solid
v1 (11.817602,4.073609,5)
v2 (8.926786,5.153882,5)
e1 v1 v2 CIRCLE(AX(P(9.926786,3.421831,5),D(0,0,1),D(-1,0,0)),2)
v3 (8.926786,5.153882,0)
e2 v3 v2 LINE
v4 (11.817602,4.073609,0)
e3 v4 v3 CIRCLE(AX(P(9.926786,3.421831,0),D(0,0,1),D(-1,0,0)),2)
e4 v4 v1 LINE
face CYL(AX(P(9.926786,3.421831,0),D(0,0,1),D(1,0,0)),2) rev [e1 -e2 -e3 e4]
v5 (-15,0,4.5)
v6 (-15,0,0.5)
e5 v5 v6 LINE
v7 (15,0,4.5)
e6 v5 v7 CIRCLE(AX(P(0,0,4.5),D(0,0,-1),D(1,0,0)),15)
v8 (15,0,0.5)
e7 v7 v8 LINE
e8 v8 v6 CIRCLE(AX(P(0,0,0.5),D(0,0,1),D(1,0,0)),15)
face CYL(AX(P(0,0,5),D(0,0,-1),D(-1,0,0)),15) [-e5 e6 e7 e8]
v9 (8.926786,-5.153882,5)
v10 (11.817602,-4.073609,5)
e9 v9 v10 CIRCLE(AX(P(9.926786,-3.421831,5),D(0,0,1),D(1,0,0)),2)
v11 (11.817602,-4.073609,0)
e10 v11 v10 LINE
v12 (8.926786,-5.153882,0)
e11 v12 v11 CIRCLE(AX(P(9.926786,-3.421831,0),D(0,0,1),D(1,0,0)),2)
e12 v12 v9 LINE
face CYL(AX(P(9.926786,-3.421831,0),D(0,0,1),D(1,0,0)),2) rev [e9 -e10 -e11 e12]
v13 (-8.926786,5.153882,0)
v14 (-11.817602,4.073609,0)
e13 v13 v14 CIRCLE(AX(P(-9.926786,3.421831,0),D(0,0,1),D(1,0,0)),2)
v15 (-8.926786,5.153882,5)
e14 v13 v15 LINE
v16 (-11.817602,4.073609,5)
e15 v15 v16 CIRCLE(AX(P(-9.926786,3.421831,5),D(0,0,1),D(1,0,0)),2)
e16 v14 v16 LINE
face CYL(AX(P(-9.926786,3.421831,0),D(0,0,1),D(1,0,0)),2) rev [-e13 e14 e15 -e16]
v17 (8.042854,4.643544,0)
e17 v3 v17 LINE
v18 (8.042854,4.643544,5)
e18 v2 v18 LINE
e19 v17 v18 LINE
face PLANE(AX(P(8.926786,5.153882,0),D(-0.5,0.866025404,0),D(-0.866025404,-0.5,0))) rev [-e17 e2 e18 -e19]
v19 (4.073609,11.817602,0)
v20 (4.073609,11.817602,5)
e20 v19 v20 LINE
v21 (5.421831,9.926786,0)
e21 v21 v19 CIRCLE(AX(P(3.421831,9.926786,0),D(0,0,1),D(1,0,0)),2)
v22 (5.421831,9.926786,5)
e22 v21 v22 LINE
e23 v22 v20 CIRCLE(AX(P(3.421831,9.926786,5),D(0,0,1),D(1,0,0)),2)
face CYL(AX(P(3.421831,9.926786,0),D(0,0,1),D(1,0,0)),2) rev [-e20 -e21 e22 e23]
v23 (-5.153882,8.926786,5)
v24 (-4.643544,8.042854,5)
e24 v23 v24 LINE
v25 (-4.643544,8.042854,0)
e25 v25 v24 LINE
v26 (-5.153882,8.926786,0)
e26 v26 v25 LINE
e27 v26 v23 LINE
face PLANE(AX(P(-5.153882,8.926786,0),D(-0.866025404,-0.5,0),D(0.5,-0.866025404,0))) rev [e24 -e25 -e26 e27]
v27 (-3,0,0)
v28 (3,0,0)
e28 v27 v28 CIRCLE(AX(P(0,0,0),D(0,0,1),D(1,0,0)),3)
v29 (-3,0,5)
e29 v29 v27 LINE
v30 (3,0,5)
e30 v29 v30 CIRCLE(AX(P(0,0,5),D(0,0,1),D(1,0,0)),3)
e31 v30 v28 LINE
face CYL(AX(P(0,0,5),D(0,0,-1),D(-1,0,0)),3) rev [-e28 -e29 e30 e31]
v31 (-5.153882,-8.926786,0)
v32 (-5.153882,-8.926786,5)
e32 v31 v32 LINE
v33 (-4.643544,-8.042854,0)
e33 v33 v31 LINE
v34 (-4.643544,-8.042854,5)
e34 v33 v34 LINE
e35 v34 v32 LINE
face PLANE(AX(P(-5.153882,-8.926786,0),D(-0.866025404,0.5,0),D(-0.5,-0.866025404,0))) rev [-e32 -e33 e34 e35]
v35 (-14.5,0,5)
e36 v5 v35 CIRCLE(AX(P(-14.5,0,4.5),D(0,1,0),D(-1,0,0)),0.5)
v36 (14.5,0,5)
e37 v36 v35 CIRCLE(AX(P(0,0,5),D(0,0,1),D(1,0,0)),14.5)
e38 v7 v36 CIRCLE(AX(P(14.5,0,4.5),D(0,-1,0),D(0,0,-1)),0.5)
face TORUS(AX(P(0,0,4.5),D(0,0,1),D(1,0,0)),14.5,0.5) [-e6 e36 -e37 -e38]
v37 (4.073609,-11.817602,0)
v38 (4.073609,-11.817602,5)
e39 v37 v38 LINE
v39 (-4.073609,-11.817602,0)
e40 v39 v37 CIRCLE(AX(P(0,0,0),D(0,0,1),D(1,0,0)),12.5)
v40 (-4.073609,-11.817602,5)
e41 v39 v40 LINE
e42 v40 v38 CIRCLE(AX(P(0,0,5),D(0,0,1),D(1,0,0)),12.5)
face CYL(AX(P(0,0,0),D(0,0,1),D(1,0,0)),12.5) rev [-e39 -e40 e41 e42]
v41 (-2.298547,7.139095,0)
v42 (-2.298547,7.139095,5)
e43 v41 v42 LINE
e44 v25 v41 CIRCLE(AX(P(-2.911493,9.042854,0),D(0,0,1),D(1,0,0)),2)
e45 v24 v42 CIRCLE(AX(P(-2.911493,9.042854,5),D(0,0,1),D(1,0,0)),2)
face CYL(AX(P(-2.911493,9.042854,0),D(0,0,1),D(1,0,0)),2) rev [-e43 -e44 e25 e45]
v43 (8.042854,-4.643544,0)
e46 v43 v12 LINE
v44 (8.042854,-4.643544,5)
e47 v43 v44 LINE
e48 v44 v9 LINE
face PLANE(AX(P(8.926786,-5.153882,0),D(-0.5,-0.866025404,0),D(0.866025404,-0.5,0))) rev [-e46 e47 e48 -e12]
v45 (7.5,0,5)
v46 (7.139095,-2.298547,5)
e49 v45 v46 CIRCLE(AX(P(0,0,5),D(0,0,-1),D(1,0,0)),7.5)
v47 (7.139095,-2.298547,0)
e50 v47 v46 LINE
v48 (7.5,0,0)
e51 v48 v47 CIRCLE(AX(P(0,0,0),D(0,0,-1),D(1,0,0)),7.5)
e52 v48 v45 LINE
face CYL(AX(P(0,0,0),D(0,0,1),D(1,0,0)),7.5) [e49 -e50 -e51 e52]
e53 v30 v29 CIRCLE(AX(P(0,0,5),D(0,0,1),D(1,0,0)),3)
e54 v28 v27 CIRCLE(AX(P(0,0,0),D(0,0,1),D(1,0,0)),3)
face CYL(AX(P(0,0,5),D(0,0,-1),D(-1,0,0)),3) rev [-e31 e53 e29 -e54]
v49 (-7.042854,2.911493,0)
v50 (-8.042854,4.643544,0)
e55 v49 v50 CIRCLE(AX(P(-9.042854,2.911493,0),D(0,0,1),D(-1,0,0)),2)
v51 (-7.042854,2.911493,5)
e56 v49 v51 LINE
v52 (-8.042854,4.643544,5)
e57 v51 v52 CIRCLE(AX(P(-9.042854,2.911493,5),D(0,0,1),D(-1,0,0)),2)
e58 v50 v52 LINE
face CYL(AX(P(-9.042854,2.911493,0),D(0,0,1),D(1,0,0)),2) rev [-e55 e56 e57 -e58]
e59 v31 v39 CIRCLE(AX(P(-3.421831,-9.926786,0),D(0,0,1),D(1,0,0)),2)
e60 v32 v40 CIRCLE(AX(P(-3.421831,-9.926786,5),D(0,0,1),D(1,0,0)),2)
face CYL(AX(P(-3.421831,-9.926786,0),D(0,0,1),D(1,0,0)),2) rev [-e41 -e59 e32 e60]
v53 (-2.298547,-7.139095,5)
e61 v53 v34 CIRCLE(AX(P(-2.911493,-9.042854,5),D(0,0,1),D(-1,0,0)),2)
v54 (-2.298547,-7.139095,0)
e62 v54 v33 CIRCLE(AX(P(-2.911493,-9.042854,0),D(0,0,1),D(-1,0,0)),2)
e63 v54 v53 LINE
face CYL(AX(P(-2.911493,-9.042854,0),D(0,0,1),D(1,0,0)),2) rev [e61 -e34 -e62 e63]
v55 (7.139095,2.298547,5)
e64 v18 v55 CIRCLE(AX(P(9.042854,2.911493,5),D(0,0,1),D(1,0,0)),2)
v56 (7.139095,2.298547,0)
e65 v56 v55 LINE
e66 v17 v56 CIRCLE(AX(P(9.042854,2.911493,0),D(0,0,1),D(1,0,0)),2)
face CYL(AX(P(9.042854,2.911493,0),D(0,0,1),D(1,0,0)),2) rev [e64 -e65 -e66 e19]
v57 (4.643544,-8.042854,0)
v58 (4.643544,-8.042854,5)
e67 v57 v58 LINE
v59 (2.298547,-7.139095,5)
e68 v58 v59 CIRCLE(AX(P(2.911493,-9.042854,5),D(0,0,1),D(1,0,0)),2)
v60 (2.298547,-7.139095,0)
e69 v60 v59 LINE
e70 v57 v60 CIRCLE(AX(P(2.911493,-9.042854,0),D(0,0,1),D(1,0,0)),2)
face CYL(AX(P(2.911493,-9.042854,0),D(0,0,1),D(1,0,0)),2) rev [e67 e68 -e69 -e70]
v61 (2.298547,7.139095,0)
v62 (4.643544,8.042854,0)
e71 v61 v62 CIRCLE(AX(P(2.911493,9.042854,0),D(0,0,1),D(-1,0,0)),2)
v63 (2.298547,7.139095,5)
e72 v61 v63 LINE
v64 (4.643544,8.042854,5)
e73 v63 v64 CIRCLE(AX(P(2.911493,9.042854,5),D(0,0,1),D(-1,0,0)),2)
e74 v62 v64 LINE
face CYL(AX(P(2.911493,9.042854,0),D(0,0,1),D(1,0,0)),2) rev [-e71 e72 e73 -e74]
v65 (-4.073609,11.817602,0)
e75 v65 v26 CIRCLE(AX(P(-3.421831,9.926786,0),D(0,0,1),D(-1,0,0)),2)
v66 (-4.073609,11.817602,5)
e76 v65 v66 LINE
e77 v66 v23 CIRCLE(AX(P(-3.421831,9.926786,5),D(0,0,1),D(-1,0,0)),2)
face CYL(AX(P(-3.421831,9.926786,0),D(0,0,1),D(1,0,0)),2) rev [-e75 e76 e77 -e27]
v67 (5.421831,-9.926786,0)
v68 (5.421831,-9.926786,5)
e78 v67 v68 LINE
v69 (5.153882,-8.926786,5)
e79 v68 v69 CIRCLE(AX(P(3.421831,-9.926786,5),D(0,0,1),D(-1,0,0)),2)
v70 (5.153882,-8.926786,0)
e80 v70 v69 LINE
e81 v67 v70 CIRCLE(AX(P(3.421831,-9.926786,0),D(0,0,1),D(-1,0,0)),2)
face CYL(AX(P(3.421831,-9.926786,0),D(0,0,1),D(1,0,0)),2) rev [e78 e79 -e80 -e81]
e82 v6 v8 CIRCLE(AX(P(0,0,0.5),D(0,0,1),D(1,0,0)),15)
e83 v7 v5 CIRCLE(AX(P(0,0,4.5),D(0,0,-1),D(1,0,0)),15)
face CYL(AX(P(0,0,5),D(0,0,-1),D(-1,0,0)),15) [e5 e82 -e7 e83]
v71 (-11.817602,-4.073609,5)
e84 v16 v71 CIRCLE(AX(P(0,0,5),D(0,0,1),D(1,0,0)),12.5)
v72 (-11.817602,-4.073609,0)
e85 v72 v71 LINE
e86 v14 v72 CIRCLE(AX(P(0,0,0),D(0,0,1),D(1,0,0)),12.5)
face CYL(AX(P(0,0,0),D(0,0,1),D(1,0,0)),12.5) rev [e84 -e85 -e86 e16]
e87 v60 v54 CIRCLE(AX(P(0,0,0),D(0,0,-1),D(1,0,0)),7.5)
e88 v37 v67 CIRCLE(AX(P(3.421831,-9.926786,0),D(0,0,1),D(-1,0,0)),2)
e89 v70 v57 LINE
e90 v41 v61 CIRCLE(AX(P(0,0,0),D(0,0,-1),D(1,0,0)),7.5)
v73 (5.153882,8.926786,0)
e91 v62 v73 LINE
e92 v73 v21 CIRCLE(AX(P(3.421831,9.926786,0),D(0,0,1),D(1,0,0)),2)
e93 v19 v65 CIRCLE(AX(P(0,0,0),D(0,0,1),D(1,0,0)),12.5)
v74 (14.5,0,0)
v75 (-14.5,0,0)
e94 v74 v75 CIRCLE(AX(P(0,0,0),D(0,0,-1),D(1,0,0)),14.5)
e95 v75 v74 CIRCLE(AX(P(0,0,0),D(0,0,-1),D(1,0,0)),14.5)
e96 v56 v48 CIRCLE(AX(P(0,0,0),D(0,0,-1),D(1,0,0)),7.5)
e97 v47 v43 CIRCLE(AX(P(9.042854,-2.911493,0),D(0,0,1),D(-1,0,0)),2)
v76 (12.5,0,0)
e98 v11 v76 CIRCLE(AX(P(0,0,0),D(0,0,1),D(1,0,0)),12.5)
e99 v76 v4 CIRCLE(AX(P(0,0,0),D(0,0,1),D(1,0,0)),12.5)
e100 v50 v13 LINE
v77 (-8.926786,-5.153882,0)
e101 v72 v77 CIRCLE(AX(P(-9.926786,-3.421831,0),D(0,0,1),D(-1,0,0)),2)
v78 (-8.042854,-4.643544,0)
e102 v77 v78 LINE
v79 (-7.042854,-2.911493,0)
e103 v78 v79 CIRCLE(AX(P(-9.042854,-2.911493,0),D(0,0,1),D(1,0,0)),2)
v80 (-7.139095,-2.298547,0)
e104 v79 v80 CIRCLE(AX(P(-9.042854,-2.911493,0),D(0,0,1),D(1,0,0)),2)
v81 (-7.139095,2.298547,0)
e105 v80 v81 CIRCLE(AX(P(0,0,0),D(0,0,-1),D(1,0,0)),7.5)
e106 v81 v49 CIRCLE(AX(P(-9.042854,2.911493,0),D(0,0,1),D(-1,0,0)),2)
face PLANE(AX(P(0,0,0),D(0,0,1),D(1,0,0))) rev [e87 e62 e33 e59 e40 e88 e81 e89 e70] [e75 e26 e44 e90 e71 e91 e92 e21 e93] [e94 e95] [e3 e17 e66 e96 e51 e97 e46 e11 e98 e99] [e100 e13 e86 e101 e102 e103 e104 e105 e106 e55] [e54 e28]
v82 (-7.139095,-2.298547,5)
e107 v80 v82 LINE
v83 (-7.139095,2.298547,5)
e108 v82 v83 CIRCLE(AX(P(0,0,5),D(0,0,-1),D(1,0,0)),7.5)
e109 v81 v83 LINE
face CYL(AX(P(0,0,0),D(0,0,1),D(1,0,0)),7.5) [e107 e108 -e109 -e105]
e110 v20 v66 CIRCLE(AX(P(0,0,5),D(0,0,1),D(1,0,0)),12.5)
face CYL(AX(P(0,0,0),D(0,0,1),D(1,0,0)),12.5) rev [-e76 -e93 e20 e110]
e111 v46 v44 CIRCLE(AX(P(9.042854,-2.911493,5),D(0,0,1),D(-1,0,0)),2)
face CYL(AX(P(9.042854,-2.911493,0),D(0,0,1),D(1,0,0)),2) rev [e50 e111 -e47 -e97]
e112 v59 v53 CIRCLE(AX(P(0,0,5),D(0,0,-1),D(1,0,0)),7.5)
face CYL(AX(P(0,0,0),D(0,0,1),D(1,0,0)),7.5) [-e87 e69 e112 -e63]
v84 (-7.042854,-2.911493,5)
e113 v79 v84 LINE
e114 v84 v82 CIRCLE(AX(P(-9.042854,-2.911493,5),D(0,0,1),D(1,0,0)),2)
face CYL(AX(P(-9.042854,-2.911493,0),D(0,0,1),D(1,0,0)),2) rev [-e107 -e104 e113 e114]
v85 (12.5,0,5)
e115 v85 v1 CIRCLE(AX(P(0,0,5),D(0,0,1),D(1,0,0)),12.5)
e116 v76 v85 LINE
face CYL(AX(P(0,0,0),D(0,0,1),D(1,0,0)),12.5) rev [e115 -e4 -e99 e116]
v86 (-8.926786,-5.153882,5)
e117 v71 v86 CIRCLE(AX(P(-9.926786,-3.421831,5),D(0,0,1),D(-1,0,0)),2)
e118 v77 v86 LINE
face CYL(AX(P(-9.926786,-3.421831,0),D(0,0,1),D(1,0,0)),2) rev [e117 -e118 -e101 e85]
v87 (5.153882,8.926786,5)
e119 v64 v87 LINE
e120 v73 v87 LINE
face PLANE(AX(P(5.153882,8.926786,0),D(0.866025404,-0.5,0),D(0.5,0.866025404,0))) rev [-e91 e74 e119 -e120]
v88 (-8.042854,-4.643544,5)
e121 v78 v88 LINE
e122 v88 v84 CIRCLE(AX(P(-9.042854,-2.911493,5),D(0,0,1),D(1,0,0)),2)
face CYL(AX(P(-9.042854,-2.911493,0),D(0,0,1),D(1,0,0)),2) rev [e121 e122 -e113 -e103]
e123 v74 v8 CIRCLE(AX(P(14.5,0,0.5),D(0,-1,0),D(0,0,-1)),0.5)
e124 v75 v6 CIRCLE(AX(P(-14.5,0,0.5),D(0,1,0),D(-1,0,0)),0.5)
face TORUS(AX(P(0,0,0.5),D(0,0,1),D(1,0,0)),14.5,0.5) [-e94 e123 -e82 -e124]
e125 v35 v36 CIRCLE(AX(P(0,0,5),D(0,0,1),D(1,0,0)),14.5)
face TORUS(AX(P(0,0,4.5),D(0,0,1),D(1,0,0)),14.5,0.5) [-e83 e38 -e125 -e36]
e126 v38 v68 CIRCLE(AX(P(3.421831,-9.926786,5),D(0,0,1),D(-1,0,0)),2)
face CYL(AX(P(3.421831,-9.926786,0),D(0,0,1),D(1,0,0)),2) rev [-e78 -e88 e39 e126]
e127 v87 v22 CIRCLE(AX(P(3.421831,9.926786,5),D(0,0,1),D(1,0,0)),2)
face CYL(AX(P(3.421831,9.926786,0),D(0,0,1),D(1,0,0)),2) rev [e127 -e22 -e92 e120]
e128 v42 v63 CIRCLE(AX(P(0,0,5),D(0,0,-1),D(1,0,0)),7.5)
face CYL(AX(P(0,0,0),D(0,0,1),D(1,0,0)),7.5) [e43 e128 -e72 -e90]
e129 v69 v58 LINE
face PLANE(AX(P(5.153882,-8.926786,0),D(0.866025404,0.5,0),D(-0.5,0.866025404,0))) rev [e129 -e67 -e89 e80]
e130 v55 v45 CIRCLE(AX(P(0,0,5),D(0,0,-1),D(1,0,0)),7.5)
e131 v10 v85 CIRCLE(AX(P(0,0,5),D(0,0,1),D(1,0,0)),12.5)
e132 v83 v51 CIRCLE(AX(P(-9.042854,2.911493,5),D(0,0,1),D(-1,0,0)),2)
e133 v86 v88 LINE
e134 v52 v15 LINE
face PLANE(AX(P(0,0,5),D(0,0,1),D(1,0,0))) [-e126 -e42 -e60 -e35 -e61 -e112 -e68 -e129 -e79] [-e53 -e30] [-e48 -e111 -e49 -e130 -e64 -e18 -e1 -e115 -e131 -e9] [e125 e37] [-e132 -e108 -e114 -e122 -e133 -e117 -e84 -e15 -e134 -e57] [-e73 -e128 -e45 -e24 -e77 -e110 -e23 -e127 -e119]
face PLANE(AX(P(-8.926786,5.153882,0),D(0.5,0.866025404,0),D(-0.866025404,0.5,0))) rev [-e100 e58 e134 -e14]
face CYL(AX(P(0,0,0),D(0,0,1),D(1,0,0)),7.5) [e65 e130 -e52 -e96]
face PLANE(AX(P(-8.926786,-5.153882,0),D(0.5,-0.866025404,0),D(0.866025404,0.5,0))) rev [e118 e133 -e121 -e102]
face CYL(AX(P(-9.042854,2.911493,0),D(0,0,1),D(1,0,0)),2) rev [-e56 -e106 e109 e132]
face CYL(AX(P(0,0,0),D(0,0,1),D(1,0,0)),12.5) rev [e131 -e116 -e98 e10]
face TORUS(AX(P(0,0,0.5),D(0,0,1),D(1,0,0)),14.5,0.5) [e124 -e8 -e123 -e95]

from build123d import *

# Parameters (mm, degrees)
SKETCH1_R           = 15
SKETCH1_R_2         = 3
BOSS_EXTRUDE1_DEPTH = 5
CUT_EXTRUDE1_DEPTH  = 5
FILLET1_R           = 0.5


with BuildPart() as part:
    # Sketch1 → Boss-Extrude1 (new body)
    with BuildSketch(Plane.XY):
        Circle(SKETCH1_R)
        Circle(SKETCH1_R_2, mode=Mode.SUBTRACT)
    extrude(amount=BOSS_EXTRUDE1_DEPTH)

    # Sketch2 → Cut-Extrude1 (cut)
    with BuildSketch(Plane.XY.offset(5)):
        with BuildLine():
            Line((-5.153882032, 8.926785536), (-4.643543905, 8.042853971))
            ThreePointArc((-4.643543905, 8.042853971), (-3.630724563, 7.176652991), (-2.298547182, 7.13909524))
            ThreePointArc((-2.298547182, 7.13909524), (0, 7.5), (2.298547182, 7.13909524))
            ThreePointArc((2.298547182, 7.13909524), (3.630724563, 7.176652991), (4.643543905, 8.042853971))
            Line((4.643543905, 8.042853971), (5.153882032, 8.926785536))
            ThreePointArc((5.153882032, 8.926785536), (5.295294304, 10.626882735), (4.073608601, 11.817601828))
            ThreePointArc((4.073608601, 11.817601828), (0, 12.5), (-4.073608601, 11.817601828))
            ThreePointArc((-4.073608601, 11.817601828), (-5.295294304, 10.626882735), (-5.153882032, 8.926785536))
        make_face()
        with BuildLine():
            Line((8.926785536, 5.153882032), (8.042853971, 4.643543905))
            ThreePointArc((8.042853971, 4.643543905), (7.176652991, 3.630724563), (7.13909524, 2.298547182))
            ThreePointArc((7.13909524, 2.298547182), (7.5, 0), (7.13909524, -2.298547182))
            ThreePointArc((7.13909524, -2.298547182), (7.176652991, -3.630724563), (8.042853971, -4.643543905))
            Line((8.042853971, -4.643543905), (8.926785536, -5.153882032))
            ThreePointArc((8.926785536, -5.153882032), (10.626882735, -5.295294304), (11.817601828, -4.073608601))
            ThreePointArc((11.817601828, -4.073608601), (12.5, 0), (11.817601828, 4.073608601))
            ThreePointArc((11.817601828, 4.073608601), (10.626882735, 5.295294304), (8.926785536, 5.153882032))
        make_face()
        with BuildLine():
            Line((5.153882032, -8.926785536), (4.643543905, -8.042853971))
            ThreePointArc((4.643543905, -8.042853971), (3.630724563, -7.176652991), (2.298547182, -7.13909524))
            ThreePointArc((2.298547182, -7.13909524), (0, -7.5), (-2.298547182, -7.13909524))
            ThreePointArc((-2.298547182, -7.13909524), (-3.630724563, -7.176652991), (-4.643543905, -8.042853971))
            Line((-4.643543905, -8.042853971), (-5.153882032, -8.926785536))
            ThreePointArc((-5.153882032, -8.926785536), (-5.295294304, -10.626882735), (-4.073608601, -11.817601828))
            ThreePointArc((-4.073608601, -11.817601828), (0, -12.5), (4.073608601, -11.817601828))
            ThreePointArc((4.073608601, -11.817601828), (5.295294304, -10.626882735), (5.153882032, -8.926785536))
        make_face()
        with BuildLine():
            Line((-8.926785536, -5.153882032), (-8.042853971, -4.643543905))
            ThreePointArc((-8.042853971, -4.643543905), (-7.176652991, -3.630724563), (-7.13909524, -2.298547182))
            ThreePointArc((-7.13909524, -2.298547182), (-7.5, 0), (-7.13909524, 2.298547182))
            ThreePointArc((-7.13909524, 2.298547182), (-7.176652991, 3.630724563), (-8.042853971, 4.643543905))
            Line((-8.042853971, 4.643543905), (-8.926785536, 5.153882032))
            ThreePointArc((-8.926785536, 5.153882032), (-10.626882735, 5.295294304), (-11.817601828, 4.073608601))
            ThreePointArc((-11.817601828, 4.073608601), (-12.5, 0), (-11.817601828, -4.073608601))
            ThreePointArc((-11.817601828, -4.073608601), (-10.626882735, -5.295294304), (-8.926785536, -5.153882032))
        make_face()
    extrude(amount=-CUT_EXTRUDE1_DEPTH, mode=Mode.SUBTRACT)

    # Fillet1
    fillet1_edges = [part.edges().sort_by_distance(p)[0] for p in [
        (-15, 0, 0),
        (-15, 0, 5),
    ]]
    fillet(fillet1_edges, radius=FILLET1_R)


solid = part.part
